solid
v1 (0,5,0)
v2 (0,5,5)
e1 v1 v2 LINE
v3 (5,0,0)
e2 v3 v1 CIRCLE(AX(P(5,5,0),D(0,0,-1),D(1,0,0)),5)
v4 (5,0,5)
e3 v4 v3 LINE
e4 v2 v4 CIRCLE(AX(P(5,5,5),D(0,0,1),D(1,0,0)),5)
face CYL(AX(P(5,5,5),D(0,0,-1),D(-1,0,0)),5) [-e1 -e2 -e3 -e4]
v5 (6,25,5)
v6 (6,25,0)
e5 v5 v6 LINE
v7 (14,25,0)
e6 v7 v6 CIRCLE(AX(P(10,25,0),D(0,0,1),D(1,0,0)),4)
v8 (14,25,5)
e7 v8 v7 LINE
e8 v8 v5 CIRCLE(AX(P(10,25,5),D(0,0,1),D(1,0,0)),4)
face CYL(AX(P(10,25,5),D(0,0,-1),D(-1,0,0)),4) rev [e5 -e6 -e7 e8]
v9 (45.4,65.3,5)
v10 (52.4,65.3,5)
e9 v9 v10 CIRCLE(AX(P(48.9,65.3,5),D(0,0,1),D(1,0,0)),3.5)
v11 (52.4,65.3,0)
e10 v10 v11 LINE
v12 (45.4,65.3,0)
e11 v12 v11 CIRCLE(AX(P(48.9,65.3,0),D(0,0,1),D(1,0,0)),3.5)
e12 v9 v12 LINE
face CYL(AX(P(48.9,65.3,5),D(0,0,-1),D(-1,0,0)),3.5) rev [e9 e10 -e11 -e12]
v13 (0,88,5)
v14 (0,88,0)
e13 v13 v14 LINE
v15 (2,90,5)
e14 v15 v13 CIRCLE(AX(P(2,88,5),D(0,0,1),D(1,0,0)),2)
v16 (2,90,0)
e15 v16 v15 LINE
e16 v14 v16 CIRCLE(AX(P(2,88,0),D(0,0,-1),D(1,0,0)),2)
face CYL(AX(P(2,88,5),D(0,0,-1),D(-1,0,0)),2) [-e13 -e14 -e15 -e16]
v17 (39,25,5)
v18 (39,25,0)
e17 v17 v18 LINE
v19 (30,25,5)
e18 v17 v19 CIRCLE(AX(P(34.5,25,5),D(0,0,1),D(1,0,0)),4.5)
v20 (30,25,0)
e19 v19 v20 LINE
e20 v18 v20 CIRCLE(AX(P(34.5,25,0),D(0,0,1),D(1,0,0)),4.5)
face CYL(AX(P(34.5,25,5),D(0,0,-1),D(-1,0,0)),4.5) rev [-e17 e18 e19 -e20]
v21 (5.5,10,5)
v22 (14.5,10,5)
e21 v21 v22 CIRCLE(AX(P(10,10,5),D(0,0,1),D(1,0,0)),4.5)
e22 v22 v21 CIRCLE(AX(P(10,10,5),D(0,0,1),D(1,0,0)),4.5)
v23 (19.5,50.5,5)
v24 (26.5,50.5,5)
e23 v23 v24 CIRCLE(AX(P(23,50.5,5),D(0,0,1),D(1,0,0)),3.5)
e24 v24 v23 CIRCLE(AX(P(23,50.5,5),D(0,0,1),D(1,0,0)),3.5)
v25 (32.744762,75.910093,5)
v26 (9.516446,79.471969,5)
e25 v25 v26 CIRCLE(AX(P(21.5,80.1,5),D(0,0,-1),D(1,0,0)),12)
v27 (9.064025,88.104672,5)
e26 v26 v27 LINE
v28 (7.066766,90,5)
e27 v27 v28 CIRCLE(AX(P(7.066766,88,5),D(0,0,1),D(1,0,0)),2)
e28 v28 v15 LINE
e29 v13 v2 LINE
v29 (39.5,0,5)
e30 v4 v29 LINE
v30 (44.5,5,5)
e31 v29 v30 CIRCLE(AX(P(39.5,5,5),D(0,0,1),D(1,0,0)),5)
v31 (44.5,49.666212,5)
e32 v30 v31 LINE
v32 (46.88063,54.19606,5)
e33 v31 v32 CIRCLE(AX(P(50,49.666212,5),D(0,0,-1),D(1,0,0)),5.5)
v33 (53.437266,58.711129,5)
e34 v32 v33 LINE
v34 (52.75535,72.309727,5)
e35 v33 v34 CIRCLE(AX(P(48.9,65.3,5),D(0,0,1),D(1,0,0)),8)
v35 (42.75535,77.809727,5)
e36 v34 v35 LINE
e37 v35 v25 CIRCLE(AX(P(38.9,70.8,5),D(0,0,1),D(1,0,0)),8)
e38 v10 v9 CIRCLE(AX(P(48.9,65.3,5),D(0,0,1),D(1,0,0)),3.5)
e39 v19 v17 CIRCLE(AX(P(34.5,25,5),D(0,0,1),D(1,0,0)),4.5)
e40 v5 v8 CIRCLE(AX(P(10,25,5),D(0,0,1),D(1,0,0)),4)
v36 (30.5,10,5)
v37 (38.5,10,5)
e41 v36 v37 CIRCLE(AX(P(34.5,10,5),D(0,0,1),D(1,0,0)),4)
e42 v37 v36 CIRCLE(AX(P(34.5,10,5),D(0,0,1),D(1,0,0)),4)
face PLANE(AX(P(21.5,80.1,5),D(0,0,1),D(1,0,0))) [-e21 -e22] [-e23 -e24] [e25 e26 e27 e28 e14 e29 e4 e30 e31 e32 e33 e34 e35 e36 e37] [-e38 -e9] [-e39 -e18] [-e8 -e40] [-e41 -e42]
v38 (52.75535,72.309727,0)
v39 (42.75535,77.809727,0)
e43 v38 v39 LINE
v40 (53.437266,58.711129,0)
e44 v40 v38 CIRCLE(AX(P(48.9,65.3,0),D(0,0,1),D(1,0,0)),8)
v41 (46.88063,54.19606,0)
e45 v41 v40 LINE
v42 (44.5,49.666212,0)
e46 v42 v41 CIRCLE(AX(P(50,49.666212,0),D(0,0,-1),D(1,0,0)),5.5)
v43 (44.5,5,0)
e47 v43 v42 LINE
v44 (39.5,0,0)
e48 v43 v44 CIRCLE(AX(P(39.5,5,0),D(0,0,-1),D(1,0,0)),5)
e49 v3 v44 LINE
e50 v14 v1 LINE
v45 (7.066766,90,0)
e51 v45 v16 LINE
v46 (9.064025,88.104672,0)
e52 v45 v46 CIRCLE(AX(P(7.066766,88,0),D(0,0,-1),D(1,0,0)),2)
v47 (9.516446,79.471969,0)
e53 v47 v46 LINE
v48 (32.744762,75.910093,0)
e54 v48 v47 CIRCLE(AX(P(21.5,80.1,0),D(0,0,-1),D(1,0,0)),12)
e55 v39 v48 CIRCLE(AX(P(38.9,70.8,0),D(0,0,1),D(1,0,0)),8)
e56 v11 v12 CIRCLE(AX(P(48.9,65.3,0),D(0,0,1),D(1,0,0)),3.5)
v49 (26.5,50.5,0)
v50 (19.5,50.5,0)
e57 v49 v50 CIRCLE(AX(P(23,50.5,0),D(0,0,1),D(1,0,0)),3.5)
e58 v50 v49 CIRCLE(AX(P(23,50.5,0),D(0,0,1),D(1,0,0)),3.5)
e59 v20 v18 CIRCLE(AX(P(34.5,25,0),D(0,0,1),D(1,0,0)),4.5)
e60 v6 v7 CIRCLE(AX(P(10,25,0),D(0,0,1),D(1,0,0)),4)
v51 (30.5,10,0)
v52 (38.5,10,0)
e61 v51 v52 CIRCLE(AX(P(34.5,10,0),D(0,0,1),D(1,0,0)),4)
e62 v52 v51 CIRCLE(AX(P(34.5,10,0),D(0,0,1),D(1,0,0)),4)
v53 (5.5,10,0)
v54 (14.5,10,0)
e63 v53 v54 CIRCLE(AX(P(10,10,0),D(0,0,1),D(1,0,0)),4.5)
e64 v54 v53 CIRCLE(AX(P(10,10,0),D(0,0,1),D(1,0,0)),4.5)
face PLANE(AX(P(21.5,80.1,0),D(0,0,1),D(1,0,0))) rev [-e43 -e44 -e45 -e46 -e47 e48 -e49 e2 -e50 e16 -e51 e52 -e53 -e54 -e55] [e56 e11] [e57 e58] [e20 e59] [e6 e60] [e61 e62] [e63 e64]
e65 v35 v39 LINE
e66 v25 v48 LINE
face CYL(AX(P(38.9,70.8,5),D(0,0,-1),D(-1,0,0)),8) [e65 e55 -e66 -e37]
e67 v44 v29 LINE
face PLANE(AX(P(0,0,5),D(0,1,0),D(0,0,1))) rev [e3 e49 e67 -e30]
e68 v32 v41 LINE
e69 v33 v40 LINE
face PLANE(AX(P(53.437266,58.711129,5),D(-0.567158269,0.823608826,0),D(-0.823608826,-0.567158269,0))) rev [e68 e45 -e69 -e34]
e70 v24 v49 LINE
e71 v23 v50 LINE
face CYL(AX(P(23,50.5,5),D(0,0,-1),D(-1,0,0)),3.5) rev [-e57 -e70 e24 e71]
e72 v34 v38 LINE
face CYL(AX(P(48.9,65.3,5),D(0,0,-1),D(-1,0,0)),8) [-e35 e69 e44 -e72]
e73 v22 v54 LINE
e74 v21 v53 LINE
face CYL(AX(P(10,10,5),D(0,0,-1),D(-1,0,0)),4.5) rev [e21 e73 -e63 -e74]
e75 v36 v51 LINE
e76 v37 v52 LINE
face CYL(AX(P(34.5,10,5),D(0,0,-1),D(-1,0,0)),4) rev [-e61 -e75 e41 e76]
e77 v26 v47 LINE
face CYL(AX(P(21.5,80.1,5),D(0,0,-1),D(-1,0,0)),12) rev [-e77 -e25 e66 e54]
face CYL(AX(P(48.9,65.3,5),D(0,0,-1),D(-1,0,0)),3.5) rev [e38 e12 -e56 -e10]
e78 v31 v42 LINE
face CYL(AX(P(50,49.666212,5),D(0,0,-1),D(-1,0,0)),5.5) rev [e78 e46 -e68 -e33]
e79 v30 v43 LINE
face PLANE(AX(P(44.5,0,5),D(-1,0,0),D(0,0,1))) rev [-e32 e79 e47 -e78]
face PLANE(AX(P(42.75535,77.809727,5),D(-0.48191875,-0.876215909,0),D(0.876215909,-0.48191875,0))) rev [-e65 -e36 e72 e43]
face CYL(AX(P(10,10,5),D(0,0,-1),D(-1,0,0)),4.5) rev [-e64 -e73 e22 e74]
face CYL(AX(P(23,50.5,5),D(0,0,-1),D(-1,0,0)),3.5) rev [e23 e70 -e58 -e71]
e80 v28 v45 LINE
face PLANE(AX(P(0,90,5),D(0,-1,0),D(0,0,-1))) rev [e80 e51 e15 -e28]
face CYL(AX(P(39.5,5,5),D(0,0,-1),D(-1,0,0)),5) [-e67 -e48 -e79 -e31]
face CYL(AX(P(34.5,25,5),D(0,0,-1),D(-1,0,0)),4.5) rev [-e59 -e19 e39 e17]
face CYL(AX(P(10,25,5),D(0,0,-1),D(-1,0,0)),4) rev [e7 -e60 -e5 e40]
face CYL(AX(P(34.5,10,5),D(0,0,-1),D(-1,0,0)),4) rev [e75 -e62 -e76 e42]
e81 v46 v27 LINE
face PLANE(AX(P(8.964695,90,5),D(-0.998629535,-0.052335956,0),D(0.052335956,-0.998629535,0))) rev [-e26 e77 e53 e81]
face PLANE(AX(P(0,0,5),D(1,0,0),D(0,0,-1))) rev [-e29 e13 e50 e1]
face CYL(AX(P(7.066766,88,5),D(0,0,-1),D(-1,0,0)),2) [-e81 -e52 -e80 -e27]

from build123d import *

# Parameters (mm, degrees)
SKETCH1_R           = 3.5
SKETCH1_R_2         = 4.5
SKETCH1_R_3         = 4
BOSS_EXTRUDE1_DEPTH = 5
FILLET1_R           = 2
FILLET2_R           = 5


with BuildPart() as part:
    # Sketch1 → Boss-Extrude1 (new body)
    with BuildSketch(Plane.XY):
        with BuildLine():
            Line((8.964694833, 90), (9.516445583, 79.471968525))
            ThreePointArc((9.516445583, 79.471968525), (19.681156059, 68.23864229), (32.744762205, 75.910092728))
            ThreePointArc((32.744762205, 75.910092728), (37.408516237, 78.659737666), (42.755349998, 77.809727269))
            Line((42.755349998, 77.809727269), (52.755349998, 72.309727269))
            ThreePointArc((52.755349998, 72.309727269), (56.88996042, 65.700665064), (53.437266153, 58.711129395))
            Line((53.437266153, 58.711129395), (46.88062952, 54.196060385))
            ThreePointArc((46.88062952, 54.196060385), (45.131399706, 52.224869926), (44.5, 49.666211844))
            Line((44.5, 49.666211844), (44.5, 0))
            Line((44.5, 0), (0, 0))
            Line((0, 0), (0, 90))
            Line((0, 90), (8.964694833, 90))
        make_face()
        with Locations((48.9, 65.3)):
            Circle(SKETCH1_R, mode=Mode.SUBTRACT)
        with Locations((10, 10)):
            Circle(SKETCH1_R_2, mode=Mode.SUBTRACT)
        with Locations((10, 25)):
            Circle(SKETCH1_R_3, mode=Mode.SUBTRACT)
        with Locations((34.5, 10)):
            Circle(SKETCH1_R_3, mode=Mode.SUBTRACT)
        with Locations((34.5, 25)):
            Circle(SKETCH1_R_2, mode=Mode.SUBTRACT)
        with Locations((23, 50.5)):
            Circle(SKETCH1_R, mode=Mode.SUBTRACT)
    extrude(amount=BOSS_EXTRUDE1_DEPTH)

    # Fillet1
    fillet1_edges = [part.edges().sort_by_distance(p)[0] for p in [
        (0, 90, 2.5),
        (8.964694833, 90, 2.5),
    ]]
    fillet(fillet1_edges, radius=FILLET1_R)

    # Fillet2
    fillet2_edges = [part.edges().sort_by_distance(p)[0] for p in [
        (44.5, 0, 2.5),
        (0, 0, 2.5),
    ]]
    fillet(fillet2_edges, radius=FILLET2_R)


solid = part.part
